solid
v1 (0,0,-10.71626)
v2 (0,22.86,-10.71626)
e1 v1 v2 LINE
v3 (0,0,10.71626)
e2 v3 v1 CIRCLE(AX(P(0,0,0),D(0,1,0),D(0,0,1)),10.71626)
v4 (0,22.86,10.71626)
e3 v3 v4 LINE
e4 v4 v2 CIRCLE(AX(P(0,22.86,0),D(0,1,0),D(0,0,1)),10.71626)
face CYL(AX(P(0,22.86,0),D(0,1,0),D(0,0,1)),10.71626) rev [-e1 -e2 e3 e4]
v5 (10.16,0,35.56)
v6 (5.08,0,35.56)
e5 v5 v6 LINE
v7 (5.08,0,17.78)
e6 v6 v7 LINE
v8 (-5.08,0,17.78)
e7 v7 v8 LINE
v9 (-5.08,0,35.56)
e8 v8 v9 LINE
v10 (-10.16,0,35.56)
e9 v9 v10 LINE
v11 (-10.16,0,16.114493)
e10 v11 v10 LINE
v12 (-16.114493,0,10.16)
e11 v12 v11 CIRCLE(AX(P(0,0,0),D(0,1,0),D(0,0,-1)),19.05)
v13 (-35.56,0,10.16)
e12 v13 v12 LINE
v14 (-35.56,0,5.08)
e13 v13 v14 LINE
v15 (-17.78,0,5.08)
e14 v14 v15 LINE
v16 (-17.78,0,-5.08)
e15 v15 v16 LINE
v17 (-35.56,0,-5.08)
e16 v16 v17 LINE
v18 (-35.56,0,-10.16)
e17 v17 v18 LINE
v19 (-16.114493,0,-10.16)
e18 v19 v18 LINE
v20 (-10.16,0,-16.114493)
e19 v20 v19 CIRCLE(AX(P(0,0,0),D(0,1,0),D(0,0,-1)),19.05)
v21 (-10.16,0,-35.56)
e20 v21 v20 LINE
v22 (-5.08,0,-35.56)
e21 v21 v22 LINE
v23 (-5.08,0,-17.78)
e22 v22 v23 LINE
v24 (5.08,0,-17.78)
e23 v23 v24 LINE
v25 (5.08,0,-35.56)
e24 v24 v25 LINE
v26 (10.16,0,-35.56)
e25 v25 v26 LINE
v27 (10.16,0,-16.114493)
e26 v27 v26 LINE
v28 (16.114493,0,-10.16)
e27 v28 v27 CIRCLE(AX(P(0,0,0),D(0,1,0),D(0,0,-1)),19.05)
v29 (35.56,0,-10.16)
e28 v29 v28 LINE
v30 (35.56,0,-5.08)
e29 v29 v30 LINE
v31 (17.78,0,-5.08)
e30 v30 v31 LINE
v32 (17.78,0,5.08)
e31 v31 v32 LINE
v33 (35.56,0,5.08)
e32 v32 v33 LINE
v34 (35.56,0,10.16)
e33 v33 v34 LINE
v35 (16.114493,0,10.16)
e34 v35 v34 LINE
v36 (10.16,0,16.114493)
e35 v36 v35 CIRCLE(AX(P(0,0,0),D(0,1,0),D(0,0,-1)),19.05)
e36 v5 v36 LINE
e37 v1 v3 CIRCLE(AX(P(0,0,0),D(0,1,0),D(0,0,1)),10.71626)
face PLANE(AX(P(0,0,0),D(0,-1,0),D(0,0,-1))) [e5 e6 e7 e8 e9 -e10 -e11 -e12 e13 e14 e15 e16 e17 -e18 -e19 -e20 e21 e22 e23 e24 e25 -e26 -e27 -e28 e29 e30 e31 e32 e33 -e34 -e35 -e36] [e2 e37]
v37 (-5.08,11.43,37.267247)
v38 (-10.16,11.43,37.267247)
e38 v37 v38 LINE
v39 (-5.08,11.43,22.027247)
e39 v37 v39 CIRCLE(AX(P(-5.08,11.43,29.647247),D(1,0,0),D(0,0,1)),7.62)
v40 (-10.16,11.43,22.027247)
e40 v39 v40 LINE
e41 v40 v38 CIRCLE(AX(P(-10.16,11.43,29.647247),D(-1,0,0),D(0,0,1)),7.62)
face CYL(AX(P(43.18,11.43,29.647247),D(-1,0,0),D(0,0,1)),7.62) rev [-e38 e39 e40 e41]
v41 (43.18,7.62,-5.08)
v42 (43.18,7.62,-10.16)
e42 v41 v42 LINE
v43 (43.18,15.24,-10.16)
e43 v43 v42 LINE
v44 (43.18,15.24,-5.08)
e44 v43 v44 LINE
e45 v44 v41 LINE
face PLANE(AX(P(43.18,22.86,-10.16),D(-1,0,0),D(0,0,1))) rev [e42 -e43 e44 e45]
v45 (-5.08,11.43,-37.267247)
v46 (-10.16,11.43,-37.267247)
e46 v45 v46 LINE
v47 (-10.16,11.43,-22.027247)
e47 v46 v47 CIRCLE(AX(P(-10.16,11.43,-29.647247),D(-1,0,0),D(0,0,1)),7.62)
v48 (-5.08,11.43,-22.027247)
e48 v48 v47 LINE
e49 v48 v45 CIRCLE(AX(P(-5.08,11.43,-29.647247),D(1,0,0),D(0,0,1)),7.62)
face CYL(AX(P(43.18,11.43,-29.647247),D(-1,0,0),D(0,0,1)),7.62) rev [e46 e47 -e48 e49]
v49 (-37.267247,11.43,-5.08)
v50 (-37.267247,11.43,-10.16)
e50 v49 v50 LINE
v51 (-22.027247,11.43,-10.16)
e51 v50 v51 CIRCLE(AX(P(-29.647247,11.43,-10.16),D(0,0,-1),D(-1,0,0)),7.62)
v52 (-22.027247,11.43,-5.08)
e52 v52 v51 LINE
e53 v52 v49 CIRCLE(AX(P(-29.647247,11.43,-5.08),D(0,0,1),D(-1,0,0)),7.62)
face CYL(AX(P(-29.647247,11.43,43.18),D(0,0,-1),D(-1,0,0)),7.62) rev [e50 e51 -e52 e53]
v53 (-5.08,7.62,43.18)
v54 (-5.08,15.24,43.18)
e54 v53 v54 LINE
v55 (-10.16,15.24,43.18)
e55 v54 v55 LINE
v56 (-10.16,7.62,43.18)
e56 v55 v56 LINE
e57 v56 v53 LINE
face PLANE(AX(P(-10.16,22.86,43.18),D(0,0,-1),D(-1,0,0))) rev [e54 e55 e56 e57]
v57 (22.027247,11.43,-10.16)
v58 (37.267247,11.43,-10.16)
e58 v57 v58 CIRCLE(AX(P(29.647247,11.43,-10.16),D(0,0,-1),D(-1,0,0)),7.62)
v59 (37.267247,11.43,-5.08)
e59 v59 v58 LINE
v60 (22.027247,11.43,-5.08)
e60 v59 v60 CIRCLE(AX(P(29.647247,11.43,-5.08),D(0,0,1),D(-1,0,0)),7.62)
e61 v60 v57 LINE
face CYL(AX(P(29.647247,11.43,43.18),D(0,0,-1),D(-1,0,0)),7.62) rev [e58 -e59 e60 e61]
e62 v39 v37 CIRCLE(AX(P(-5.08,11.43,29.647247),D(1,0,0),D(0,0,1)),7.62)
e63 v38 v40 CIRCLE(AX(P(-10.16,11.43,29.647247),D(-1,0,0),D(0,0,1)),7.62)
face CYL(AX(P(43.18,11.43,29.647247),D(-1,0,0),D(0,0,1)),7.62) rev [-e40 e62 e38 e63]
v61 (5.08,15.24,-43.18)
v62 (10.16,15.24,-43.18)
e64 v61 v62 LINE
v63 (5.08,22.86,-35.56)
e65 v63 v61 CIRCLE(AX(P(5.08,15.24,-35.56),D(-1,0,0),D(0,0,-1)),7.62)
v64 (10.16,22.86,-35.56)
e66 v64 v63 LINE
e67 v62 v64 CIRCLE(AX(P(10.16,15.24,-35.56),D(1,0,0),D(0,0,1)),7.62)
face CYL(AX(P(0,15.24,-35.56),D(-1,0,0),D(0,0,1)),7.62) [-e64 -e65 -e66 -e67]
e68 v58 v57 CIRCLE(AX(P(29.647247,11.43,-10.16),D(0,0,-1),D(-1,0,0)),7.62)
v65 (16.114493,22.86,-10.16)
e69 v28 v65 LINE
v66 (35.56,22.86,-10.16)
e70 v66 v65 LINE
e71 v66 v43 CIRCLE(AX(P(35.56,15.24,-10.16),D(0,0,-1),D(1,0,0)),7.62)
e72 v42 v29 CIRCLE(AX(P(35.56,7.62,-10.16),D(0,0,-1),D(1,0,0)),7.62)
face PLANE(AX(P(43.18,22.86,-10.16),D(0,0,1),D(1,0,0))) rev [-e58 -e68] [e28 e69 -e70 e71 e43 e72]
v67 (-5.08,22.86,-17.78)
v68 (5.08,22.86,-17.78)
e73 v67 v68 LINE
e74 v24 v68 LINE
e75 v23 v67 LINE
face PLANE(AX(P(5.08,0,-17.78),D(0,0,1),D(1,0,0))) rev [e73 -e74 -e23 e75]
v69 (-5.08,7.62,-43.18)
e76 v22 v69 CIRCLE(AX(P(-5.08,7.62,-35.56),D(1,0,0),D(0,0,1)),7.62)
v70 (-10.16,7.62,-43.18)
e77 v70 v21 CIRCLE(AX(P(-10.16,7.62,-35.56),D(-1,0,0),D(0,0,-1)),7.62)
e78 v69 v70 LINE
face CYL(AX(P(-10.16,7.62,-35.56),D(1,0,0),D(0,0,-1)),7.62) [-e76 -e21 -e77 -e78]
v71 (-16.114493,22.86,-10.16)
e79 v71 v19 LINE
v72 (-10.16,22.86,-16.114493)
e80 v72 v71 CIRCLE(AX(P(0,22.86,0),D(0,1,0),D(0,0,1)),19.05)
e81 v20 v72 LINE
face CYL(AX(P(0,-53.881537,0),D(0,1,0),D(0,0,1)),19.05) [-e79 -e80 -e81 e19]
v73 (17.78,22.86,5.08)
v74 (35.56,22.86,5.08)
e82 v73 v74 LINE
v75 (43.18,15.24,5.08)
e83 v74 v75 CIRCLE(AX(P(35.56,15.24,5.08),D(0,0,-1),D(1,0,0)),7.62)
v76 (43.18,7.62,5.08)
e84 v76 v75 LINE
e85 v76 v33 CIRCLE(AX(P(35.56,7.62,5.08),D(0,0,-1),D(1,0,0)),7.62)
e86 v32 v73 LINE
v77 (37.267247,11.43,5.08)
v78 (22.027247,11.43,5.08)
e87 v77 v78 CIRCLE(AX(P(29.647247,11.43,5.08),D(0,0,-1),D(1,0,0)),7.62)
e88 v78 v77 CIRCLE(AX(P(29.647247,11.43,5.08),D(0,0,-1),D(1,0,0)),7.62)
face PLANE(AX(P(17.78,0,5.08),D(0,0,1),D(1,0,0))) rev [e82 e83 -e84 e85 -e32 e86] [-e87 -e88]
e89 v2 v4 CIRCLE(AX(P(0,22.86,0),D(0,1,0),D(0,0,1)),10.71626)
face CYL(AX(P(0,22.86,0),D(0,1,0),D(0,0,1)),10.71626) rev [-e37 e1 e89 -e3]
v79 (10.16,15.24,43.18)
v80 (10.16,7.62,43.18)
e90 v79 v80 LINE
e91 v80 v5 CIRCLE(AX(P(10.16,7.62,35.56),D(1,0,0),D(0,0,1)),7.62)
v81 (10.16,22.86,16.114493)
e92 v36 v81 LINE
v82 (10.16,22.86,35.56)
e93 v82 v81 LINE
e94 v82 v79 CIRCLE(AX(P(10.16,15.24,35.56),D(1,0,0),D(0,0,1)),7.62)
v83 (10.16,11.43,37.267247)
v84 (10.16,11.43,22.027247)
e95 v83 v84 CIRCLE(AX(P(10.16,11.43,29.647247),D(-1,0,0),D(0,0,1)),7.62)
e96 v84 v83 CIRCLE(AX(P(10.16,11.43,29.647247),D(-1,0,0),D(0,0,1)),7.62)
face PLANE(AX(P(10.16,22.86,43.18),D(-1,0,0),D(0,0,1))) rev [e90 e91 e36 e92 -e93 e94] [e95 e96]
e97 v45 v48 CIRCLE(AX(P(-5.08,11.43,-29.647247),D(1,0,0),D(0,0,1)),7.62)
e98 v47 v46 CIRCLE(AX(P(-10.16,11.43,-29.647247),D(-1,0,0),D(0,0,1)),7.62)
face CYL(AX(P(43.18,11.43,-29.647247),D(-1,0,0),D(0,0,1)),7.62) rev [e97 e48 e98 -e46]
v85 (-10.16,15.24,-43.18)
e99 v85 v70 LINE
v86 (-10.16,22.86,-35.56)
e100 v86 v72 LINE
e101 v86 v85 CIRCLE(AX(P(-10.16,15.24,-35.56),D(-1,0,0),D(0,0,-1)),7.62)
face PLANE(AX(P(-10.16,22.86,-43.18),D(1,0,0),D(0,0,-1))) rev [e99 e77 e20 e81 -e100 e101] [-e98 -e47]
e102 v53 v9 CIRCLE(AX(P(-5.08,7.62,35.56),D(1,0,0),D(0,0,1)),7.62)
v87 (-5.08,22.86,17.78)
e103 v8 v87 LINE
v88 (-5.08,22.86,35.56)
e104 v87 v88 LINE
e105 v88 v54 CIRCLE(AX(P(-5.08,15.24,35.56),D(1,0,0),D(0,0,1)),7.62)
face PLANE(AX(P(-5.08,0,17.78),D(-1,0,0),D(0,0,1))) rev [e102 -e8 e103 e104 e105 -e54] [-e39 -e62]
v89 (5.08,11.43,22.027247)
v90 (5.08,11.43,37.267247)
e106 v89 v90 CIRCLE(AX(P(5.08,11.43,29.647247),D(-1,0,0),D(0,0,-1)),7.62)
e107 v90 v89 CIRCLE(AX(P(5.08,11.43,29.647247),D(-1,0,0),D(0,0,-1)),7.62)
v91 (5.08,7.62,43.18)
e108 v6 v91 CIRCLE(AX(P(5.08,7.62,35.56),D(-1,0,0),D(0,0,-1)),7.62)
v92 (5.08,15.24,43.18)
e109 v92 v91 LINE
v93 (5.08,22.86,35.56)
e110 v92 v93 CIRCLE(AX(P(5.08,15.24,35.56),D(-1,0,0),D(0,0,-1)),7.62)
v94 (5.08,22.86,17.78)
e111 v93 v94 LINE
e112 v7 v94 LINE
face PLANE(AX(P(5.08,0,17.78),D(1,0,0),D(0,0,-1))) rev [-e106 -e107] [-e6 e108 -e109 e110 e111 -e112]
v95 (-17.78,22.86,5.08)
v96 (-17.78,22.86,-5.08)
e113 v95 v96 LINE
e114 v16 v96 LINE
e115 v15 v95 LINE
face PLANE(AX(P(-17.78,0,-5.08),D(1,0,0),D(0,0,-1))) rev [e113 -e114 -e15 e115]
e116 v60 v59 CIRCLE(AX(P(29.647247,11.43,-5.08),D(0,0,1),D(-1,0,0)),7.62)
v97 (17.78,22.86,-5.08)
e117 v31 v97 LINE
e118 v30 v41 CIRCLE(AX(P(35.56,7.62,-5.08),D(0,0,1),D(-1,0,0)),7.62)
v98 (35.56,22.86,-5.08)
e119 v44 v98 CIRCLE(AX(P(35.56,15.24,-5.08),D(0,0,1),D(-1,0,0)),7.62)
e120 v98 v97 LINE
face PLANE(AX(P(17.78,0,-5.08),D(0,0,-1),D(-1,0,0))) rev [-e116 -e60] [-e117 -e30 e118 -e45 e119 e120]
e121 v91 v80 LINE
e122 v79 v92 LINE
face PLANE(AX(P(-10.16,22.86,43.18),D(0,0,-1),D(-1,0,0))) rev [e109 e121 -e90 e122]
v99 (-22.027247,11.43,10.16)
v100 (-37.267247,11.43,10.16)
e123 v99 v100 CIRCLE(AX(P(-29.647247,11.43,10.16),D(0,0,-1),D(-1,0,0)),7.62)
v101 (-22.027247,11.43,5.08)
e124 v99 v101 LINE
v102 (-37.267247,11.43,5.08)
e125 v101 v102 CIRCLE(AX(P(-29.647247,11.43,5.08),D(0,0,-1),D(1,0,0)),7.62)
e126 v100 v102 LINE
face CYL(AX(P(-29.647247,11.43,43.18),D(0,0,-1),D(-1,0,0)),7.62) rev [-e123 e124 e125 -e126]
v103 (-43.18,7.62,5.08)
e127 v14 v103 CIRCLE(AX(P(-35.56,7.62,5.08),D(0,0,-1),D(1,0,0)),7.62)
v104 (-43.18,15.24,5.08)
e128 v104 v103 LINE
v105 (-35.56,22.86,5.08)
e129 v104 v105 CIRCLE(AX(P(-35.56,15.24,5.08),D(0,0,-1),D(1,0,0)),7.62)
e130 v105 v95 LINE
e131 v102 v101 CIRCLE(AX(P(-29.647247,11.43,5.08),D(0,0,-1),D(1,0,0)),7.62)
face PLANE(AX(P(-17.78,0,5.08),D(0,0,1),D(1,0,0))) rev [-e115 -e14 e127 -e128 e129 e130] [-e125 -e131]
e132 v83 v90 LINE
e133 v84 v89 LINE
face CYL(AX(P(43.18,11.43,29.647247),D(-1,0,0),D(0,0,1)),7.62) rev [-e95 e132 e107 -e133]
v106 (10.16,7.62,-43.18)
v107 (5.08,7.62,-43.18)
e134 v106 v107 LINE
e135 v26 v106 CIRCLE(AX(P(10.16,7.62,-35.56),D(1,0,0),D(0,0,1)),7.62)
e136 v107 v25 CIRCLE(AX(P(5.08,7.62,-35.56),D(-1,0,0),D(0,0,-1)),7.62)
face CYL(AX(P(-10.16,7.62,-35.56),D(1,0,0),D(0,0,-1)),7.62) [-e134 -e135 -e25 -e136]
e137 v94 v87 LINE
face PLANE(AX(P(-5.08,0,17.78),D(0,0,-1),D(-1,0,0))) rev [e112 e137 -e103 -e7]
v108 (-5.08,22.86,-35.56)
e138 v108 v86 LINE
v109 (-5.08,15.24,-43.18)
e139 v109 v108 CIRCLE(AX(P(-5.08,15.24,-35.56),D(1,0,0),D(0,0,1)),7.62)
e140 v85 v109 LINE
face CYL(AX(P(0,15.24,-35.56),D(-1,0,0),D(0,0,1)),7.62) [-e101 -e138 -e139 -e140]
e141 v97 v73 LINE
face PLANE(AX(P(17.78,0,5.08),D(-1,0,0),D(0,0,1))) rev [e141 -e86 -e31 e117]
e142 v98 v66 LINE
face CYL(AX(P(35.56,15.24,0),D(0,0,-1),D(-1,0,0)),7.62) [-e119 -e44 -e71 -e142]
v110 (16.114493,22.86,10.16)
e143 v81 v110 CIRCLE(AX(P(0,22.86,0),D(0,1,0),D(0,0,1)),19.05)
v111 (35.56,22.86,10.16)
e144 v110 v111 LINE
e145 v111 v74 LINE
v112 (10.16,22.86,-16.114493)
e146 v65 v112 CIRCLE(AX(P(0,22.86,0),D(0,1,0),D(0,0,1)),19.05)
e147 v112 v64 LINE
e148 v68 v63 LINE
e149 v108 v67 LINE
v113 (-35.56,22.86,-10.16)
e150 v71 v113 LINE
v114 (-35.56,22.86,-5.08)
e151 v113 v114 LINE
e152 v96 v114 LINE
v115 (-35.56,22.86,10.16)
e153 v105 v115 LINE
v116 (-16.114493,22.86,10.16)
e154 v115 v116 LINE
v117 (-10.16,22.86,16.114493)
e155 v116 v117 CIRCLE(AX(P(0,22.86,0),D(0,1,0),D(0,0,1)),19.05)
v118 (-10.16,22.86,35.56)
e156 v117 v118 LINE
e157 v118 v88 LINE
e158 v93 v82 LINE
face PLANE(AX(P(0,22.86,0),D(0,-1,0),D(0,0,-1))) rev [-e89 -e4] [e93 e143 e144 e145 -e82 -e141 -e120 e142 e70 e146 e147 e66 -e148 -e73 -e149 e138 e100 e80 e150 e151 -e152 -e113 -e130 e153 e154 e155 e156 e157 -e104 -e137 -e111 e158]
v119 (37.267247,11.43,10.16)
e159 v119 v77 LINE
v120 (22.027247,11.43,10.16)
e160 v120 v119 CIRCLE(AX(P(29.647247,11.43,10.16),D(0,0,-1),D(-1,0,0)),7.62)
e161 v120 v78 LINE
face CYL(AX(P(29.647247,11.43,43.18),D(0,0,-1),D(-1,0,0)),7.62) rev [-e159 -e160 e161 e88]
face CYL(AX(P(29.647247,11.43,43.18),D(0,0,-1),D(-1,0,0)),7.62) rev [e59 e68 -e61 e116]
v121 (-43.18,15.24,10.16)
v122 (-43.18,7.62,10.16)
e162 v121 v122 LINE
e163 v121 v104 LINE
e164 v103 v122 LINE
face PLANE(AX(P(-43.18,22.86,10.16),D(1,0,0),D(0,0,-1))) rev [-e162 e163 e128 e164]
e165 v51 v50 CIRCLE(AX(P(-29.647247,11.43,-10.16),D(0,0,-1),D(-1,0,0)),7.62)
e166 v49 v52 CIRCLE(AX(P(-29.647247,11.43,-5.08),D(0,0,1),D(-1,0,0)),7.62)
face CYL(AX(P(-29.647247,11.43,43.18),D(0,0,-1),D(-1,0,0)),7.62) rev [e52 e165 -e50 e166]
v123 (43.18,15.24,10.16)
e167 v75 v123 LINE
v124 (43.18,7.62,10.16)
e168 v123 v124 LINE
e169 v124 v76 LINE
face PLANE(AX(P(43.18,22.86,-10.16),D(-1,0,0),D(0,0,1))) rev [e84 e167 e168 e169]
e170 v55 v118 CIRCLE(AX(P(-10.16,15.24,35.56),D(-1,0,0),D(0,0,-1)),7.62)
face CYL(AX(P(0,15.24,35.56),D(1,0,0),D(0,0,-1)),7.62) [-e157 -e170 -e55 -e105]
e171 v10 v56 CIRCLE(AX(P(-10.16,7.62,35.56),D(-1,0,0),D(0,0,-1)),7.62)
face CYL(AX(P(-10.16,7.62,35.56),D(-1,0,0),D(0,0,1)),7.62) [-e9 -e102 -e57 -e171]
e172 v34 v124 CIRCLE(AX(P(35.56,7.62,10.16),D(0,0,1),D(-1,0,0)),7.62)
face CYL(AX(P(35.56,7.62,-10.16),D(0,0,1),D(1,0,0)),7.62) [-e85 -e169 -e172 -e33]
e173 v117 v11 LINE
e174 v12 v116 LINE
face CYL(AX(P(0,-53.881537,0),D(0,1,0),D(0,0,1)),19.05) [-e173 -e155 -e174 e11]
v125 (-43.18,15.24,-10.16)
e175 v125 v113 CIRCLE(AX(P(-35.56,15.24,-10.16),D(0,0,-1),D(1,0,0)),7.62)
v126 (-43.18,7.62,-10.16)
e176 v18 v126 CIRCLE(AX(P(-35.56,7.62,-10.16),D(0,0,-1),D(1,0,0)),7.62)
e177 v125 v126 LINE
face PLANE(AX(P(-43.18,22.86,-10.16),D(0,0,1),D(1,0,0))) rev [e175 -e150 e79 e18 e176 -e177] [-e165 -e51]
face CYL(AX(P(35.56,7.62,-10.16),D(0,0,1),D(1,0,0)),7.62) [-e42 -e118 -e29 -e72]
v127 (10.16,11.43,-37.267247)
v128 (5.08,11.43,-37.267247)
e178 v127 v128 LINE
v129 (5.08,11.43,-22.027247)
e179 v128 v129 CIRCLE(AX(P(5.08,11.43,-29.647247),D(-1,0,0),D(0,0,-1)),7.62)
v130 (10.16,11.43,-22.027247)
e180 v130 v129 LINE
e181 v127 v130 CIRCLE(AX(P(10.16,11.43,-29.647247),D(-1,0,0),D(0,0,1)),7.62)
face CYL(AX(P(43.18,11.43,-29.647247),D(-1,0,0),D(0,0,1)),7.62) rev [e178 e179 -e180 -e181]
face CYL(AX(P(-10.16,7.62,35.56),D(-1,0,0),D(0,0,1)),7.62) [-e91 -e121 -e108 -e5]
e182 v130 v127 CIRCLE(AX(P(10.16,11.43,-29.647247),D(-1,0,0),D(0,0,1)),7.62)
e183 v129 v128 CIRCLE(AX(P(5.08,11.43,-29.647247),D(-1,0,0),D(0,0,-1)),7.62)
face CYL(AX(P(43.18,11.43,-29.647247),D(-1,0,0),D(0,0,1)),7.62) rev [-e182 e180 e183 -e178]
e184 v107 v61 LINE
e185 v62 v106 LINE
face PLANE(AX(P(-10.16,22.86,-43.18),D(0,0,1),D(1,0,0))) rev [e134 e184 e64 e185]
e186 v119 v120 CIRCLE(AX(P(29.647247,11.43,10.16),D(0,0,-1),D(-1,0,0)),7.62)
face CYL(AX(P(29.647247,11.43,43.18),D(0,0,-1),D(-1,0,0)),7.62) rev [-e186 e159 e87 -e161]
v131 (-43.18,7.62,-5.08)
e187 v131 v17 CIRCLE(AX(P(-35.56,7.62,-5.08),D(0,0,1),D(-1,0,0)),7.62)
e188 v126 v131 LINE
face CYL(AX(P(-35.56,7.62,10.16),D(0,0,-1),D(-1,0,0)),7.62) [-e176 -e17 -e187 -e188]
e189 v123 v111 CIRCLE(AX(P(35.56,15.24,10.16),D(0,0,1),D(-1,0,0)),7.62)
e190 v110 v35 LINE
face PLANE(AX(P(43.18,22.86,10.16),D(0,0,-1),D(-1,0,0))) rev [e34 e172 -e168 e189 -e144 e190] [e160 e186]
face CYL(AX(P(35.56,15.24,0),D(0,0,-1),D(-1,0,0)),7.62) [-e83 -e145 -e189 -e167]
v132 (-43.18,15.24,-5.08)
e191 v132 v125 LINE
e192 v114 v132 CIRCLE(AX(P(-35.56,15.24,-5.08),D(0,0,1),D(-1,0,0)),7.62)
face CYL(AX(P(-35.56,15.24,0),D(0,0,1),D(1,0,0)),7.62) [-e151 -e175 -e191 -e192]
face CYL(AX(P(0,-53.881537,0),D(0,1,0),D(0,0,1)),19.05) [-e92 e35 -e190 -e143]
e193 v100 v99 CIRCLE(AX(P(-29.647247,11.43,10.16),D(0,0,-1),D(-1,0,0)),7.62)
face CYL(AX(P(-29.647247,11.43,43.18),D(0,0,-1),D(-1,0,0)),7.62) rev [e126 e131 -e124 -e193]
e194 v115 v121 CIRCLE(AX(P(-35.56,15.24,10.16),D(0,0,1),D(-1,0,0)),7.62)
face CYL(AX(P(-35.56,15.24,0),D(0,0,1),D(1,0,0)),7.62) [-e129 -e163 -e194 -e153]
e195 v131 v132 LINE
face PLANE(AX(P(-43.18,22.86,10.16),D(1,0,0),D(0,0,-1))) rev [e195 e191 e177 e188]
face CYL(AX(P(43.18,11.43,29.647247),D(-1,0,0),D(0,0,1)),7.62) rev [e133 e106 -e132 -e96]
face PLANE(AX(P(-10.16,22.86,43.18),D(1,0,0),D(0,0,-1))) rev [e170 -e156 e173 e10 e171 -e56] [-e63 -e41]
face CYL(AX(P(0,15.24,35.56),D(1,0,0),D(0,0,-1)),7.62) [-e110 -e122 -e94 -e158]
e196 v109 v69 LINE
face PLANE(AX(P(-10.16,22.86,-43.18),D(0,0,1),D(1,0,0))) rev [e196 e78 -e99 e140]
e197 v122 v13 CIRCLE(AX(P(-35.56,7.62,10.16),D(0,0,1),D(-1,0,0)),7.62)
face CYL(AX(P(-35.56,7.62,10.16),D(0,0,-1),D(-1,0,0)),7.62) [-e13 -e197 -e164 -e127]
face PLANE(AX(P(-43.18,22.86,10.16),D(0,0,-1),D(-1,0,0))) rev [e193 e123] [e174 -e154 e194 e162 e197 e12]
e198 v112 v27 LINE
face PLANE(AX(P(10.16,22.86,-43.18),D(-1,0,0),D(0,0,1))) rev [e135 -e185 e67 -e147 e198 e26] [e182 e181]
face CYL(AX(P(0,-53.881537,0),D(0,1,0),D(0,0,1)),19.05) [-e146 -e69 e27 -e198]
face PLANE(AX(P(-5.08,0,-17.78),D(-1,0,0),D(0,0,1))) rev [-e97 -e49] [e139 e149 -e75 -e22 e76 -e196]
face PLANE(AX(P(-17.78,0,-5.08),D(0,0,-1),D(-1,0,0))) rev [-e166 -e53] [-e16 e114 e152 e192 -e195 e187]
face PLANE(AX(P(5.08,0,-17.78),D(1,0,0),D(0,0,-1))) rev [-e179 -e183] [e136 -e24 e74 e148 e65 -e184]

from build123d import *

# Parameters (mm, degrees)
BOSS_EXTRUDE1_DEPTH     = 11.43
SKETCH2_R               = 9.525
BOSS_EXTRUDE2_DEPTH     = 11.43
SKETCH8_R               = 3.81
CUT_EXTRUDE6_DEPTH      = 37.167138399
SKETCH9_R               = 3.81
CUT_EXTRUDE7_DEPTH      = 37.167138399
F_1_2_13_TAPPED_HOLE1_D = 10.71626
SKETCH12_W              = 25.4
SKETCH12_H              = 5.08
CUT_EXTRUDE8_DEPTH      = 33.602164039
CIRPATTERN1_COUNT       = 4
FILLET1_R               = 3.81
SCALE1_SCALE            = 2


with BuildPart() as part:
    # Sketch1 → Boss-Extrude1 (new body)
    with BuildSketch(Plane(origin=(0, 0, 0), x_dir=(1, 0, 0), z_dir=(0, 1, 0))):
        Polygon((-5.08, 21.59), (5.08, 21.59), (5.08, 5.08), (21.59, 5.08), (21.59, -5.08), (5.08, -5.08), (5.08, -21.59), (-5.08, -21.59), (-5.08, -5.08), (-21.59, -5.08), (-21.59, 5.08), (-5.08, 5.08), align=None)
    extrude(amount=BOSS_EXTRUDE1_DEPTH)

    # Sketch2 → Boss-Extrude2 (add)
    with BuildSketch(Plane(origin=(0, 11.43, 0), x_dir=(1, 0, 0), z_dir=(0, 1, 0))):
        Circle(SKETCH2_R)
    extrude(amount=-BOSS_EXTRUDE2_DEPTH)

    # Sketch8 → Cut-Extrude6 (cut, through all)
    with BuildSketch(Plane.ZY.offset(5.08)):
        with Locations((14.823623369, 5.715)):
            Circle(SKETCH8_R)
        with Locations((-14.823623369, 5.715)):
            Circle(SKETCH8_R)
    extrude(amount=-CUT_EXTRUDE6_DEPTH, mode=Mode.SUBTRACT)

    # Sketch9 → Cut-Extrude7 (cut, through all)
    with BuildSketch(Plane(origin=(0, 0, -5.08), x_dir=(-1, 0, 0), z_dir=(0, 0, -1))):
        with Locations((14.823623369, 5.715)):
            Circle(SKETCH9_R)
        with Locations((-14.823623369, 5.715)):
            Circle(SKETCH9_R)
    extrude(amount=-CUT_EXTRUDE7_DEPTH, mode=Mode.SUBTRACT)

    # 1/2-13 Tapped Hole1 (through all)
    with Locations(Plane(origin=(0, 11.43, 0), x_dir=(1, 0, 0), z_dir=(0, 1, 0))):
        with Locations((0, 0)):
            Hole(F_1_2_13_TAPPED_HOLE1_D / 2)

    # Sketch12 → Cut-Extrude8 (cut, through all)
    with BuildSketch(Plane(origin=(0, 11.43, 0), x_dir=(1, 0, 0), z_dir=(0, 1, 0))):
        with Locations((-21.59, 0)):
            Rectangle(SKETCH12_W, SKETCH12_H)
    cut_extrude8 = extrude(amount=-CUT_EXTRUDE8_DEPTH, mode=Mode.SUBTRACT)

    # CirPattern1: Cut-Extrude8 ×4 about axis
    cirpattern1_axis = Axis((0, 0, 0), (0, 1, 0))
    for i in range(1, CIRPATTERN1_COUNT):
        add(cut_extrude8.rotate(cirpattern1_axis, i * 360 / CIRPATTERN1_COUNT), mode=Mode.SUBTRACT)

    # Fillet1
    fillet1_edges = [part.edges().sort_by_distance(p)[0] for p in [
        (-21.59, 0, 3.81),
        (-21.59, 11.43, 3.81),
        (21.59, 0, 3.81),
        (-3.81, 0, 21.59),
        (3.81, 0, 21.59),
        (3.81, 11.43, 21.59),
        (-21.59, 0, -3.81),
        (21.59, 0, -3.81),
        (21.59, 11.43, -3.81),
        (3.81, 0, -21.59),
        (-21.59, 11.43, -3.81),
        (-3.81, 0, -21.59),
        (-3.81, 11.43, -21.59),
        (-3.81, 11.43, 21.59),
        (21.59, 11.43, 3.81),
        (3.81, 11.43, -21.59),
    ]]
    fillet(fillet1_edges, radius=FILLET1_R)


with BuildPart() as part_1:
    # Scale1: scaled about (0, 0, 0)
    add(part.part.scale(SCALE1_SCALE))


solid = part_1.part
